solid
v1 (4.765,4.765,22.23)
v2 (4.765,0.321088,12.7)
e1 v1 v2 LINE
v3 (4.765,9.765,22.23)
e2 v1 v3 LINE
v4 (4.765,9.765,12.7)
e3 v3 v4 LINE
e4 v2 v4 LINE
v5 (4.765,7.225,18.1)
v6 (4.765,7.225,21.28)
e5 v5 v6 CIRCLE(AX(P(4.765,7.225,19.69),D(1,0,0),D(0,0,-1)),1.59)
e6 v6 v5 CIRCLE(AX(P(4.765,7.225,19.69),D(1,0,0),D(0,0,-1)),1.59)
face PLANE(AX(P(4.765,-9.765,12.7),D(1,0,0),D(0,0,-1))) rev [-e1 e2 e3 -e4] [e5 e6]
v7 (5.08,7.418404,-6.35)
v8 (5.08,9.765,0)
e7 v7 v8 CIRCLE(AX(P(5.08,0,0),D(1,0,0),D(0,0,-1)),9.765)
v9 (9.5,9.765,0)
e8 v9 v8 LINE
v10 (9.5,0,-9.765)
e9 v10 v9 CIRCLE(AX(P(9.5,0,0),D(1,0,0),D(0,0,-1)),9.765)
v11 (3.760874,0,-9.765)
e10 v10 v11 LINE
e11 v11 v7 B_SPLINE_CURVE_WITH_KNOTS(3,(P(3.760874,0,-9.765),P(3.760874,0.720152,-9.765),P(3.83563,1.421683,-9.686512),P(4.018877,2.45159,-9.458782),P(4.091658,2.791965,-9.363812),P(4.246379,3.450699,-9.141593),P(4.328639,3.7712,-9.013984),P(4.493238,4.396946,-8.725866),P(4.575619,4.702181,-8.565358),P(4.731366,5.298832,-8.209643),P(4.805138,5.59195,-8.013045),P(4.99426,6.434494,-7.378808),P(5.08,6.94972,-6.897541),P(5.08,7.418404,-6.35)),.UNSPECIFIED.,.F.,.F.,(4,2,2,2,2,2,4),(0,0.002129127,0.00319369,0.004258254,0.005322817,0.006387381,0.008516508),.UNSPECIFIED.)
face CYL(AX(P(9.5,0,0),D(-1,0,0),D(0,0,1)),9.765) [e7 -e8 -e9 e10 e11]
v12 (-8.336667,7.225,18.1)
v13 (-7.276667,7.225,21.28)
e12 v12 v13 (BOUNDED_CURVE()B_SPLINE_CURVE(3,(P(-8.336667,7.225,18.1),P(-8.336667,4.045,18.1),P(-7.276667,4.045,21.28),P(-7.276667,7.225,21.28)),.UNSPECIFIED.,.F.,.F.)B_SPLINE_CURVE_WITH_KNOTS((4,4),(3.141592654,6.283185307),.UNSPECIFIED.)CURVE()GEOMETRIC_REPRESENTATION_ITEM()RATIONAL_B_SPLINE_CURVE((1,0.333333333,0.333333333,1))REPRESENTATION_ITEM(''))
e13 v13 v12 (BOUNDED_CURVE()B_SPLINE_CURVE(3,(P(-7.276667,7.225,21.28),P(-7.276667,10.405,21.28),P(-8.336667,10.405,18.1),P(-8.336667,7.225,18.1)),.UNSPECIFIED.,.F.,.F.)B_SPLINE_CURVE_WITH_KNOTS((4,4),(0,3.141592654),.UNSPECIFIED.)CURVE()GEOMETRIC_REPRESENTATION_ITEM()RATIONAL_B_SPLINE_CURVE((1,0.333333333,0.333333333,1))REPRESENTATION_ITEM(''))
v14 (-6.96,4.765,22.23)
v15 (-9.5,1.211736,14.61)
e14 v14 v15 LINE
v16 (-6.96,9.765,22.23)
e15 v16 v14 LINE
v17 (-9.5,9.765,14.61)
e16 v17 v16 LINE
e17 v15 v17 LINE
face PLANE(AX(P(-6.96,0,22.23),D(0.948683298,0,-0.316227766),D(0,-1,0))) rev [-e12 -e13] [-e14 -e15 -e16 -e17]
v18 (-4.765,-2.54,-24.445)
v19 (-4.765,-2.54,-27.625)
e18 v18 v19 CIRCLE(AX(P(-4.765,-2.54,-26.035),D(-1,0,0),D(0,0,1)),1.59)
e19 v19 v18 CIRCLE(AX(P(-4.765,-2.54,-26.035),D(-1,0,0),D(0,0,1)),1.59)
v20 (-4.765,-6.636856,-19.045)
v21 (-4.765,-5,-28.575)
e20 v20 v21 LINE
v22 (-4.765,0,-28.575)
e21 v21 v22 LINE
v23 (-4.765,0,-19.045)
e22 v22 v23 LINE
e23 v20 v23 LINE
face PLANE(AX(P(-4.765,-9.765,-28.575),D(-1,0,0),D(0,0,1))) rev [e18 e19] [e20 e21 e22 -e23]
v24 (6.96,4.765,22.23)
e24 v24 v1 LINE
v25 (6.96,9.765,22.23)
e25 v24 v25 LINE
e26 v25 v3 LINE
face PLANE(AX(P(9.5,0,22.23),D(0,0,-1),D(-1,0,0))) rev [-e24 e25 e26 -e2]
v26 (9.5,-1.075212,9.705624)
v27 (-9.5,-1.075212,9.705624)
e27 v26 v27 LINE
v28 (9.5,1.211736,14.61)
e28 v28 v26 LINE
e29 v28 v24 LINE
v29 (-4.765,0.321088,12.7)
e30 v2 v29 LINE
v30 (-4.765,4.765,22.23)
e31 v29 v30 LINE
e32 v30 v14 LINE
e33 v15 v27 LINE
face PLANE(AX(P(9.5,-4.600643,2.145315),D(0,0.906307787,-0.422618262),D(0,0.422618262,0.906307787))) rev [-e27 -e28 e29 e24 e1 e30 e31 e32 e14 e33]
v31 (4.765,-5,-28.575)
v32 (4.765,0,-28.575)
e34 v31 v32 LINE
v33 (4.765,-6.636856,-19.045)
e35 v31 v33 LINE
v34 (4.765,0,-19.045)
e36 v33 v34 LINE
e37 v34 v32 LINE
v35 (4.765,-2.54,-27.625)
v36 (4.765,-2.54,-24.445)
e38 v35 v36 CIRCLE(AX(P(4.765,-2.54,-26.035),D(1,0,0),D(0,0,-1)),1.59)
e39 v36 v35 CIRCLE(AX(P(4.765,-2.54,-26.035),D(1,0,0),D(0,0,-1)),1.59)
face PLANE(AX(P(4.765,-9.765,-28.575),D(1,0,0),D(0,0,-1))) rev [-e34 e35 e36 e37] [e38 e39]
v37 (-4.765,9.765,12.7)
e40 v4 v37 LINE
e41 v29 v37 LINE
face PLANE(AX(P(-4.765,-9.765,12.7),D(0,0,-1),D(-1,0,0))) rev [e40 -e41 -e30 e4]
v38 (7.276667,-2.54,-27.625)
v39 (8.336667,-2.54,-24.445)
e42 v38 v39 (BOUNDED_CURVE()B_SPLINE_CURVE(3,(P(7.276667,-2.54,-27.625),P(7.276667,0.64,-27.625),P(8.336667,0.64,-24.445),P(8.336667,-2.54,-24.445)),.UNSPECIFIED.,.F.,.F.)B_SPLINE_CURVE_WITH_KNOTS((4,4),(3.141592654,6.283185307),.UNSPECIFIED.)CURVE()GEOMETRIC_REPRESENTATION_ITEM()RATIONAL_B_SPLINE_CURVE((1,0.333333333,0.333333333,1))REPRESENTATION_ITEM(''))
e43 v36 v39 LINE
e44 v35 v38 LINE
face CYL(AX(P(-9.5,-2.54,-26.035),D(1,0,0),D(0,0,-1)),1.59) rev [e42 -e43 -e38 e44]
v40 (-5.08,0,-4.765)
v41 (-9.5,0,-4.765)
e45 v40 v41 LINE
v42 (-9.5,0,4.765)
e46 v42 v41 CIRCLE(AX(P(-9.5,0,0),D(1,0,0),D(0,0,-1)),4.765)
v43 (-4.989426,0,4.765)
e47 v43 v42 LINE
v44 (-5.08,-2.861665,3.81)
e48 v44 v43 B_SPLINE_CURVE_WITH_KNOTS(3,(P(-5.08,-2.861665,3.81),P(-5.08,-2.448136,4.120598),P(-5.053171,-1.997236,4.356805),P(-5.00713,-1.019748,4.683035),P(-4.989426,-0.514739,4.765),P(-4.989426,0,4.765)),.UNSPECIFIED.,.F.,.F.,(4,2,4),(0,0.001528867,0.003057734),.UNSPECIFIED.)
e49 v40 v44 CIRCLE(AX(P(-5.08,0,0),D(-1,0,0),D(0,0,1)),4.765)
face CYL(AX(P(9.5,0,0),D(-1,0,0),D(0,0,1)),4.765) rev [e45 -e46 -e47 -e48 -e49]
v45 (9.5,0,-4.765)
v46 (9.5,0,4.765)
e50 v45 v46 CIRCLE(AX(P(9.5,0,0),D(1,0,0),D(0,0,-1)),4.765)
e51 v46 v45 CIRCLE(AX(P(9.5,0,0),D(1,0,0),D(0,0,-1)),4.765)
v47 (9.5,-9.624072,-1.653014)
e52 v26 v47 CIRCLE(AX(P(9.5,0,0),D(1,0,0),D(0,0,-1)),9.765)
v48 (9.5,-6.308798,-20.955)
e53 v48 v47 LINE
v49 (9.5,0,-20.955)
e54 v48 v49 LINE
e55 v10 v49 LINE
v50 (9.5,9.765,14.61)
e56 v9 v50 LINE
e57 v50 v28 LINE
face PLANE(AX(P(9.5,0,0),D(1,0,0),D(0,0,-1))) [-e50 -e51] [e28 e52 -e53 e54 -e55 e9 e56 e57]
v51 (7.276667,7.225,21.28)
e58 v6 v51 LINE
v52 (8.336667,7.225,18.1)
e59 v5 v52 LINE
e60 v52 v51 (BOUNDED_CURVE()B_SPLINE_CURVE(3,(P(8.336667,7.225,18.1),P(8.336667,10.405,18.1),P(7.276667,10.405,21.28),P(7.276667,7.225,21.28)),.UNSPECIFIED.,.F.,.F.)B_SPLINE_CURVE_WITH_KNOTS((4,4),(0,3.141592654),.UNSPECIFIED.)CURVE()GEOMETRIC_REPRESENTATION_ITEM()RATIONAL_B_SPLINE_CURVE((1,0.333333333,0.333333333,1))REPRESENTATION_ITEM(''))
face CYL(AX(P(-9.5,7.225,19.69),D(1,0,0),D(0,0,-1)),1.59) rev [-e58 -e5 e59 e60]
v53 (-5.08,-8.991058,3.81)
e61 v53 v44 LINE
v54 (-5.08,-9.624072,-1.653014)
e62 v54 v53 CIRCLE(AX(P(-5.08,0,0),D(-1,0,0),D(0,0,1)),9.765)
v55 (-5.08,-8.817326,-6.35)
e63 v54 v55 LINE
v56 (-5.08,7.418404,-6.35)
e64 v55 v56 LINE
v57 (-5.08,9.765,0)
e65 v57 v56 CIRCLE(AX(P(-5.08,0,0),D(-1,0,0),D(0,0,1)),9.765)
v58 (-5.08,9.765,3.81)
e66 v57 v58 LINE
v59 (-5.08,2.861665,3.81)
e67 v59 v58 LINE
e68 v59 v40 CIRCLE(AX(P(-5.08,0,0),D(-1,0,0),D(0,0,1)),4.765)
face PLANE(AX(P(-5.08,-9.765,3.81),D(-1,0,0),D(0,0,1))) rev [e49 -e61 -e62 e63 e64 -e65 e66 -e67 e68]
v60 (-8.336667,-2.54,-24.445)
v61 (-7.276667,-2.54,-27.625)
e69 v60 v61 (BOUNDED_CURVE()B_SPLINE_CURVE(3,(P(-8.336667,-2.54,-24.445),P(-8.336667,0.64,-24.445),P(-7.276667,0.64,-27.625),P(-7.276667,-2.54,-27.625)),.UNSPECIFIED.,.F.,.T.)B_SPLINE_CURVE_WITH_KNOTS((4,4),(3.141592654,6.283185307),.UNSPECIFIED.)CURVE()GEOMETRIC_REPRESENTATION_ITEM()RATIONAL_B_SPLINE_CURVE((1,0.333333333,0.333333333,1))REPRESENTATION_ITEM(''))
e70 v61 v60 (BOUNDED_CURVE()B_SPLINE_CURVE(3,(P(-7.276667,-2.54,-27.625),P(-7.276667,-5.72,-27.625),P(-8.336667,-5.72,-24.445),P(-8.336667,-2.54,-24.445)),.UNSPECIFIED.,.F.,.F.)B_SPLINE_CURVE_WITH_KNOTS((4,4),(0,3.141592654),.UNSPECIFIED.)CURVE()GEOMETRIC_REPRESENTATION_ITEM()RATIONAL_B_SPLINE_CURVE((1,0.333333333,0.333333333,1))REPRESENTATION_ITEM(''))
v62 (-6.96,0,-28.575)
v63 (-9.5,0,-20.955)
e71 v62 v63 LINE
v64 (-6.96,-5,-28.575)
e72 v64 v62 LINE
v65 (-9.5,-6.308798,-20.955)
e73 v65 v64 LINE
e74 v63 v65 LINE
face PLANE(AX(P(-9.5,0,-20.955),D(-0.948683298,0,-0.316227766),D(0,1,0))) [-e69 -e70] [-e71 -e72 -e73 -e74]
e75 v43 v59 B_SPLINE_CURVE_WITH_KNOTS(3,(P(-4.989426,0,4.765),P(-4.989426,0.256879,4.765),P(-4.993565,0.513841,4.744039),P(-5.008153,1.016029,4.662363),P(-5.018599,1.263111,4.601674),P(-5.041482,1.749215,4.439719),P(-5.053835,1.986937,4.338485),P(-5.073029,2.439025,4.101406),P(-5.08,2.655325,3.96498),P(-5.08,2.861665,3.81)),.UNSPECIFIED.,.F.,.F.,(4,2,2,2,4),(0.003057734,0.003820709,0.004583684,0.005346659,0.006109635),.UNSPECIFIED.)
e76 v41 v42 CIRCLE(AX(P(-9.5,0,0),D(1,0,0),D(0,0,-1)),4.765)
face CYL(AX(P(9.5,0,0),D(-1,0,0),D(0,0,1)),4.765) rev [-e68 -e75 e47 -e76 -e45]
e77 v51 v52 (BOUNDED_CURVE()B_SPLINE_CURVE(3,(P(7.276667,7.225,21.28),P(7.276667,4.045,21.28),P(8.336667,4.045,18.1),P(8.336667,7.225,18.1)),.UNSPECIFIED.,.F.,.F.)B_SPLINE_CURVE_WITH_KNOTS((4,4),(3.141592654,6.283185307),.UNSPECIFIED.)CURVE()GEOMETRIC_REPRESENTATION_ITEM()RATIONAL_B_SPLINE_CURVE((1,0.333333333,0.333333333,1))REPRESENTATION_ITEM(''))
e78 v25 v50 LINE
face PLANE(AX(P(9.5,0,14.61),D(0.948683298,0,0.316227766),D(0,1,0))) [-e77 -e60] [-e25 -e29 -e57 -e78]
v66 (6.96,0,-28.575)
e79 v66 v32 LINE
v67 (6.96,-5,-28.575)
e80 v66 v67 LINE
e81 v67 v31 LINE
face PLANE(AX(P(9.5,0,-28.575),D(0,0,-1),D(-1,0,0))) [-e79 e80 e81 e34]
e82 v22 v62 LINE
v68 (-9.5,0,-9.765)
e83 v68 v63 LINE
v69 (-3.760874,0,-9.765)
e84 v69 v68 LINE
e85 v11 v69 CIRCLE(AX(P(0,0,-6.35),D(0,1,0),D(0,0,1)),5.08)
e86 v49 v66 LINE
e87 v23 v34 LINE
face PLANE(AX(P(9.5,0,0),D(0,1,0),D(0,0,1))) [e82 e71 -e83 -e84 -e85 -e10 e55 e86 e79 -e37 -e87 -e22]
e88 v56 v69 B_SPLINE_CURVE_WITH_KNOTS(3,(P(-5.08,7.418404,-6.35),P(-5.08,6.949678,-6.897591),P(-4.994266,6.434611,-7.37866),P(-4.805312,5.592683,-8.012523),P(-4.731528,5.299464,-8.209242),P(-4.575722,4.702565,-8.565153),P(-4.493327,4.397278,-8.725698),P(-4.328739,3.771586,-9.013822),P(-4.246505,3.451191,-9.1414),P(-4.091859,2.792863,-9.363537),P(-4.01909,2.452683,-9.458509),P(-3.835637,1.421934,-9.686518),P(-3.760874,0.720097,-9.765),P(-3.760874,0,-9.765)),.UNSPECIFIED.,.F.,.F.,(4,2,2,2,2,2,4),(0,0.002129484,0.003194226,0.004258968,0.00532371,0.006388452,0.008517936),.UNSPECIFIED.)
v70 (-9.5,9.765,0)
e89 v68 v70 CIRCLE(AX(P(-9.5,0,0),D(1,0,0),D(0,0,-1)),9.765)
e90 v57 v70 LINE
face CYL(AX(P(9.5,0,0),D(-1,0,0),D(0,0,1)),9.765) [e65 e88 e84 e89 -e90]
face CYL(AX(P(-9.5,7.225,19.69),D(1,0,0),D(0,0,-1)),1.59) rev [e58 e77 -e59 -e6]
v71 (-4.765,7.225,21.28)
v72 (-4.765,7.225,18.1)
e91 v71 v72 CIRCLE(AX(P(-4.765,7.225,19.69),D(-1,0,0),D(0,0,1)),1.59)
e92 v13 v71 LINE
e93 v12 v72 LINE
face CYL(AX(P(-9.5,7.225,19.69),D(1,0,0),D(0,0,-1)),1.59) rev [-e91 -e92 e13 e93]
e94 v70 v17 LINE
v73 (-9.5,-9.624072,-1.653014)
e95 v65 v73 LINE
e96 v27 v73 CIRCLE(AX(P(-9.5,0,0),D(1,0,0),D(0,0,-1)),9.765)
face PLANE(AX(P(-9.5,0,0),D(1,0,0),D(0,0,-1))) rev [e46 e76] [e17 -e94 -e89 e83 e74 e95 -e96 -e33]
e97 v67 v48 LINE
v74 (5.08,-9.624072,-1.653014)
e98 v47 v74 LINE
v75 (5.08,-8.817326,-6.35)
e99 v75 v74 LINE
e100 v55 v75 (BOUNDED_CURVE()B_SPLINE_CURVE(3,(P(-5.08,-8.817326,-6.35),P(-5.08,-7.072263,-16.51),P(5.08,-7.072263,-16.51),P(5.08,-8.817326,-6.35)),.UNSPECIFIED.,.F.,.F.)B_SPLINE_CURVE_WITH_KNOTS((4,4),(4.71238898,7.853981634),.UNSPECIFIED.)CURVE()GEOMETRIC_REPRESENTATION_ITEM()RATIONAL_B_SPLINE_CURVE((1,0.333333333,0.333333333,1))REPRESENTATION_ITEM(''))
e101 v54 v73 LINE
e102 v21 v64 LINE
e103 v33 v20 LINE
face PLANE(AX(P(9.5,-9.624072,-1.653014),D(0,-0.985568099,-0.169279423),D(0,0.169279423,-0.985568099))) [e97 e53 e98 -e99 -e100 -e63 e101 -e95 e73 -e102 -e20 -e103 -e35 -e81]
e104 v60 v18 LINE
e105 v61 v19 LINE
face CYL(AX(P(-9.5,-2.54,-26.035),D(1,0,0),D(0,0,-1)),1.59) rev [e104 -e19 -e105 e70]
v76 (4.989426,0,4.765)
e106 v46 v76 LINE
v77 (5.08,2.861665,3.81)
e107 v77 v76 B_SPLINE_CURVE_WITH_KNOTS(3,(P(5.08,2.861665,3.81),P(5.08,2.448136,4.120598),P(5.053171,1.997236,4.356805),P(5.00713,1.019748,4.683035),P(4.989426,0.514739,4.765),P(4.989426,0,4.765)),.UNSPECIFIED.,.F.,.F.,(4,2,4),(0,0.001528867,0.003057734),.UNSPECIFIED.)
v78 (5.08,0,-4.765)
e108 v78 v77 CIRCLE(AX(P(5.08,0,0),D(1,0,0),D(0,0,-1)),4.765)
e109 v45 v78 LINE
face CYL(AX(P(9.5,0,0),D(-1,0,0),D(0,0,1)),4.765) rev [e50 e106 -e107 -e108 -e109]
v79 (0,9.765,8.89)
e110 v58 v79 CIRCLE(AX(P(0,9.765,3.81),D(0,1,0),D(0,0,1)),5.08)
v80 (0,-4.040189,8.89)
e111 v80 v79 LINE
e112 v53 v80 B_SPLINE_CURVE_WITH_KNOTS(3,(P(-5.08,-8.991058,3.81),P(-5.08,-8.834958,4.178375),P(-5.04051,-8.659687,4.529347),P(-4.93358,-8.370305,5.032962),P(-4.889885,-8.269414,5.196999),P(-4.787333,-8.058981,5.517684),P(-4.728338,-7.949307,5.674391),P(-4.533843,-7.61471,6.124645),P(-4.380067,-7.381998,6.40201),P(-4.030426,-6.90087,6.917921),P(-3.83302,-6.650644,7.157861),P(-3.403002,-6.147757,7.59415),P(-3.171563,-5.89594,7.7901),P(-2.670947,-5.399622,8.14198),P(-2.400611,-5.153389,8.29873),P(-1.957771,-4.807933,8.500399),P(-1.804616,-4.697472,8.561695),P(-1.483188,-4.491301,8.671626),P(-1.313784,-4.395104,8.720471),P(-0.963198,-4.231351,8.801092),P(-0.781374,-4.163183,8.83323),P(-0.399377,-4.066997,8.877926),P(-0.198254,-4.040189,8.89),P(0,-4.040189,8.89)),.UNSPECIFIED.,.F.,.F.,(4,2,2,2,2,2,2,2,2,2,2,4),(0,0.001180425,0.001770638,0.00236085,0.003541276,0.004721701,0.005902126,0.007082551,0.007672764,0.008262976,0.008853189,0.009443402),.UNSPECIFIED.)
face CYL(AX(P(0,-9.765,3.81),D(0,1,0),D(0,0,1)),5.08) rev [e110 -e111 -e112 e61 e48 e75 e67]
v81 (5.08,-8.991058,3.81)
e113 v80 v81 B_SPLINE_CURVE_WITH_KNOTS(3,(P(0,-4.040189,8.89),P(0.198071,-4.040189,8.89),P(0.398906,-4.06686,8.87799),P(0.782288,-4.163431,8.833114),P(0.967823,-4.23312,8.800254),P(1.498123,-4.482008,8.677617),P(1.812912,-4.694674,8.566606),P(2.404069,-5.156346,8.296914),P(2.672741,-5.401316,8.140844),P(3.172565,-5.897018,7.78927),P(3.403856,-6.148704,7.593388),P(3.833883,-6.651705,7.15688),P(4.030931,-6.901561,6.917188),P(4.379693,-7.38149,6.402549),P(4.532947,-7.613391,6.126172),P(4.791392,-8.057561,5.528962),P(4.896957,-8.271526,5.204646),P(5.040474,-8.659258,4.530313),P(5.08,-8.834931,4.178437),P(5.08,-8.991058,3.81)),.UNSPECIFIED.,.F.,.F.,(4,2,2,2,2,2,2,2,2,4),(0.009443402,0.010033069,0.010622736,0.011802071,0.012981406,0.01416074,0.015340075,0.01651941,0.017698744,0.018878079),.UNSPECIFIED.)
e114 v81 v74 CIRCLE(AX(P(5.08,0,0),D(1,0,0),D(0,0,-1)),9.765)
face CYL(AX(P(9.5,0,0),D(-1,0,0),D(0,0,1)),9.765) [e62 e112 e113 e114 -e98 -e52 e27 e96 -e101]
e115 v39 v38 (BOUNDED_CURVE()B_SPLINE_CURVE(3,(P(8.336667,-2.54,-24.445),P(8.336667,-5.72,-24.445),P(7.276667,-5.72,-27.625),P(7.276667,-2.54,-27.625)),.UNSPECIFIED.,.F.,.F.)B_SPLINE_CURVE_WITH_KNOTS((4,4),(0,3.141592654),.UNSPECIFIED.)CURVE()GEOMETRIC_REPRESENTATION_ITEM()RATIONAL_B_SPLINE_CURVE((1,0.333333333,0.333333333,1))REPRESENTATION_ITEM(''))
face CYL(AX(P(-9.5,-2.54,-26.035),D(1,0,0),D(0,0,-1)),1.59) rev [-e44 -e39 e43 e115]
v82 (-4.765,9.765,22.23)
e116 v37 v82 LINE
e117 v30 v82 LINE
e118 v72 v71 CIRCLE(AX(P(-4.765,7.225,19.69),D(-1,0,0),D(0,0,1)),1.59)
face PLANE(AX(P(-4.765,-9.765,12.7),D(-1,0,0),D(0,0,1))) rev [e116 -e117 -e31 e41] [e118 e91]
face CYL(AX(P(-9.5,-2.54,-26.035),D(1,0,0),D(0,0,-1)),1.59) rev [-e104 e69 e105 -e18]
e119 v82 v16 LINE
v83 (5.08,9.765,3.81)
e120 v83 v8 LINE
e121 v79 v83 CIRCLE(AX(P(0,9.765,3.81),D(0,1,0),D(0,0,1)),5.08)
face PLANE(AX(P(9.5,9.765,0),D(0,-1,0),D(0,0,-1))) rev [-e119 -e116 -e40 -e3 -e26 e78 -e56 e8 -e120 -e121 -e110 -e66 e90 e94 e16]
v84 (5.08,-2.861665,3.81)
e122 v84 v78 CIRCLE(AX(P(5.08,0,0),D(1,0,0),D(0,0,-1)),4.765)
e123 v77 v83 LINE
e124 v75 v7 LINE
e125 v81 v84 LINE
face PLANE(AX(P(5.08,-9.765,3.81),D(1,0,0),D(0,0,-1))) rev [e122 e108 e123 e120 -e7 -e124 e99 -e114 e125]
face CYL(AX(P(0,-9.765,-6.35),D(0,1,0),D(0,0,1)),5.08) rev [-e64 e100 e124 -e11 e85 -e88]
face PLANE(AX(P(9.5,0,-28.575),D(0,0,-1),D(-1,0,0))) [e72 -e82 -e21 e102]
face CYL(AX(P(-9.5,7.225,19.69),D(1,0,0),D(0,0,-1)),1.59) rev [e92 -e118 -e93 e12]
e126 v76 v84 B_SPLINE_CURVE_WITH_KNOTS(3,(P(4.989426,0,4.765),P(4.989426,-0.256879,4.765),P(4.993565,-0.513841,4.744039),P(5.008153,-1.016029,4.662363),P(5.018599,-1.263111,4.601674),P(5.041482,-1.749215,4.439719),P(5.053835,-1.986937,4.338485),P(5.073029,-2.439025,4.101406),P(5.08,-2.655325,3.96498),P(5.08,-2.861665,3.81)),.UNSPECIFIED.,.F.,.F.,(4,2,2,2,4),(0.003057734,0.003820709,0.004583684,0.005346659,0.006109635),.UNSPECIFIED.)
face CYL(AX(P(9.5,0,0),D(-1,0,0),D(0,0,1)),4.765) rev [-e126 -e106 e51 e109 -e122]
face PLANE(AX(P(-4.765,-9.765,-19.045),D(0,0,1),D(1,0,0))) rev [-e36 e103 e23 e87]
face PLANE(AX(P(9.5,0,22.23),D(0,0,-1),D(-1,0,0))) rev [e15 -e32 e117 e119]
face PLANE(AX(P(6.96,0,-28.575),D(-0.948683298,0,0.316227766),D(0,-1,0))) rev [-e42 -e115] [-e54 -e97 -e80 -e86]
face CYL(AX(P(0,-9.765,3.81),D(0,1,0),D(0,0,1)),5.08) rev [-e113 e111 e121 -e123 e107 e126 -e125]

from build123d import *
from OCP.BRepFilletAPI import BRepFilletAPI_MakeChamfer

# Parameters (mm, degrees)
ROCKER_ARM_PROFILE_SKETCH_R  = 4.765
ROCKER_ARM_BODY_DEPTH        = 9.5
END_CHAMFER_2_54X7_62_SIZE   = 2.54
END_CHAMFER_2_54X7_62_SIZE2  = 7.62
END_CHAMFER_7_62X2_54_SIZE   = 7.62
END_CHAMFER_7_62X2_54_SIZE2  = 2.54
HUB_CUT_DEPTH                = 32.656529342
HUB_CUT_DEPTH_BACK           = 32.656529342
FORK_SLOT_CUT_DEPTH          = 32.656529403
FORK_SLOT_CUT_DEPTH_BACK     = 32.656529403
FORK_SLOT_SKETCH_W           = 9.53
FORK_SLOT_SKETCH_H           = 9.53
PIN_HOLES_2X_3_18_DEPTH      = 32.656529403
PIN_HOLES_2X_3_18_DEPTH_BACK = 32.656529403
PIN_HOLES_SKETCH_R           = 1.59


with BuildPart() as part:
    # Rocker Arm Profile Sketch → Rocker Arm Body (new, symmetric)
    with BuildSketch(Plane(origin=(0, 0, 0), x_dir=(0, 0, -1), z_dir=(1, 0, 0))):
        with BuildLine():
            ThreePointArc((9.765, 0), (6.904897718, 6.904897718), (0, 9.765))
            Line((0, 9.765), (-22.23, 9.765))
            Line((-22.23, 9.765), (-22.23, 4.765))
            Line((-22.23, 4.765), (-9.705624325, -1.075212291))
            ThreePointArc((-9.705624325, -1.075212291), (-5.872128035, -7.802136716), (1.653013564, -9.624072483))
            Line((1.653013564, -9.624072483), (28.575, -5))
            Line((28.575, -5), (28.575, 0))
            Line((28.575, 0), (9.765, 0))
        make_face()
        Circle(ROCKER_ARM_PROFILE_SKETCH_R, mode=Mode.SUBTRACT)
    extrude(amount=ROCKER_ARM_BODY_DEPTH, both=True)

    # End Chamfer 2.54x7.62: one chamfer whose edges measure the first distance from different faces: ONE call of the kernel's chamfer builder (chamfer() names one face for all edges)
    end_chamfer_2_54x7_62_edges_1 = [part.edges().sort_by_distance(p)[0] for p in [
        (-9.5, -2.5, -28.575),
    ]]
    end_chamfer_2_54x7_62_side_1 = [part.faces().sort_by_distance(p)[0] for p in [
        (0, -2.5, -28.575),
    ]]
    end_chamfer_2_54x7_62_edges_2 = [part.edges().sort_by_distance(p)[0] for p in [
        (9.5, 7.265, 22.23),
    ]]
    end_chamfer_2_54x7_62_side_2 = [part.faces().sort_by_distance(p)[0] for p in [
        (0, 7.265, 22.23),
    ]]
    end_chamfer_2_54x7_62 = BRepFilletAPI_MakeChamfer(part.part.solid().wrapped)
    for e in end_chamfer_2_54x7_62_edges_1:
        end_chamfer_2_54x7_62.Add(END_CHAMFER_2_54X7_62_SIZE, END_CHAMFER_2_54X7_62_SIZE2, e.wrapped, end_chamfer_2_54x7_62_side_1[0].wrapped)  # the first distance lies on this face
    for e in end_chamfer_2_54x7_62_edges_2:
        end_chamfer_2_54x7_62.Add(END_CHAMFER_2_54X7_62_SIZE, END_CHAMFER_2_54X7_62_SIZE2, e.wrapped, end_chamfer_2_54x7_62_side_2[0].wrapped)  # the first distance lies on this face
    add(Compound.cast(end_chamfer_2_54x7_62.Shape()), mode=Mode.REPLACE)

    # End Chamfer 7.62x2.54: one chamfer whose edges measure the first distance from different faces: ONE call of the kernel's chamfer builder (chamfer() names one face for all edges)
    end_chamfer_7_62x2_54_edges_1 = [part.edges().sort_by_distance(p)[0] for p in [
        (-9.5, 7.265, 22.23),
    ]]
    end_chamfer_7_62x2_54_side_1 = [part.faces().sort_by_distance(p)[0] for p in [
        (-9.5, -0.473958345, -15.36),
    ]]
    end_chamfer_7_62x2_54_edges_2 = [part.edges().sort_by_distance(p)[0] for p in [
        (9.5, -2.5, -28.575),
    ]]
    end_chamfer_7_62x2_54_side_2 = [part.faces().sort_by_distance(p)[0] for p in [
        (9.5, 9.291041655, 7.305),
    ]]
    end_chamfer_7_62x2_54 = BRepFilletAPI_MakeChamfer(part.part.solid().wrapped)
    for e in end_chamfer_7_62x2_54_edges_1:
        end_chamfer_7_62x2_54.Add(END_CHAMFER_7_62X2_54_SIZE, END_CHAMFER_7_62X2_54_SIZE2, e.wrapped, end_chamfer_7_62x2_54_side_1[0].wrapped)  # the first distance lies on this face
    for e in end_chamfer_7_62x2_54_edges_2:
        end_chamfer_7_62x2_54.Add(END_CHAMFER_7_62X2_54_SIZE, END_CHAMFER_7_62X2_54_SIZE2, e.wrapped, end_chamfer_7_62x2_54_side_2[0].wrapped)  # the first distance lies on this face
    add(Compound.cast(end_chamfer_7_62x2_54.Shape()), mode=Mode.REPLACE)

    # Hub Cut Sketch → Hub Cut (cut, two sides: drawn at the far end of the back side and taken through both)
    with BuildSketch(Plane(origin=(0, 0, 0), x_dir=(1, 0, 0), z_dir=(0, 1, 0)).offset(-HUB_CUT_DEPTH_BACK)):
        with BuildLine():
            Line((-5.08, -3.81), (-5.08, 6.35))
            ThreePointArc((-5.08, 6.35), (0, 11.43), (5.08, 6.35))
            Line((5.08, 6.35), (5.08, -3.81))
            ThreePointArc((5.08, -3.81), (0, -8.89), (-5.08, -3.81))
        make_face()
    extrude(amount=HUB_CUT_DEPTH + HUB_CUT_DEPTH_BACK, mode=Mode.SUBTRACT)

    # Fork Slot Sketch → Fork Slot Cut (cut, two sides: drawn at the far end of the back side and taken through both)
    with BuildSketch(Plane(origin=(0, 0, 0), x_dir=(1, 0, 0), z_dir=(0, 1, 0)).offset(-FORK_SLOT_CUT_DEPTH_BACK)):
        with Locations((0, 23.81)):
            Rectangle(FORK_SLOT_SKETCH_W, FORK_SLOT_SKETCH_H)
        with Locations((0, -17.465)):
            Rectangle(FORK_SLOT_SKETCH_W, FORK_SLOT_SKETCH_H)
    extrude(amount=FORK_SLOT_CUT_DEPTH + FORK_SLOT_CUT_DEPTH_BACK, mode=Mode.SUBTRACT)

    # Pin Holes Sketch → Pin Holes 2xØ3.18 (cut, two sides: drawn at the far end of the back side and taken through both)
    with BuildSketch(Plane(origin=(0, 0, 0), x_dir=(0, 0, -1), z_dir=(1, 0, 0)).offset(-PIN_HOLES_2X_3_18_DEPTH_BACK)):
        with Locations(Location((-19.69, 7.225, 0), (0, 0, 180))):
            Circle(PIN_HOLES_SKETCH_R)
        with Locations((26.035, -2.54)):
            Circle(PIN_HOLES_SKETCH_R)
    extrude(amount=PIN_HOLES_2X_3_18_DEPTH + PIN_HOLES_2X_3_18_DEPTH_BACK, mode=Mode.SUBTRACT)


solid = part.part
